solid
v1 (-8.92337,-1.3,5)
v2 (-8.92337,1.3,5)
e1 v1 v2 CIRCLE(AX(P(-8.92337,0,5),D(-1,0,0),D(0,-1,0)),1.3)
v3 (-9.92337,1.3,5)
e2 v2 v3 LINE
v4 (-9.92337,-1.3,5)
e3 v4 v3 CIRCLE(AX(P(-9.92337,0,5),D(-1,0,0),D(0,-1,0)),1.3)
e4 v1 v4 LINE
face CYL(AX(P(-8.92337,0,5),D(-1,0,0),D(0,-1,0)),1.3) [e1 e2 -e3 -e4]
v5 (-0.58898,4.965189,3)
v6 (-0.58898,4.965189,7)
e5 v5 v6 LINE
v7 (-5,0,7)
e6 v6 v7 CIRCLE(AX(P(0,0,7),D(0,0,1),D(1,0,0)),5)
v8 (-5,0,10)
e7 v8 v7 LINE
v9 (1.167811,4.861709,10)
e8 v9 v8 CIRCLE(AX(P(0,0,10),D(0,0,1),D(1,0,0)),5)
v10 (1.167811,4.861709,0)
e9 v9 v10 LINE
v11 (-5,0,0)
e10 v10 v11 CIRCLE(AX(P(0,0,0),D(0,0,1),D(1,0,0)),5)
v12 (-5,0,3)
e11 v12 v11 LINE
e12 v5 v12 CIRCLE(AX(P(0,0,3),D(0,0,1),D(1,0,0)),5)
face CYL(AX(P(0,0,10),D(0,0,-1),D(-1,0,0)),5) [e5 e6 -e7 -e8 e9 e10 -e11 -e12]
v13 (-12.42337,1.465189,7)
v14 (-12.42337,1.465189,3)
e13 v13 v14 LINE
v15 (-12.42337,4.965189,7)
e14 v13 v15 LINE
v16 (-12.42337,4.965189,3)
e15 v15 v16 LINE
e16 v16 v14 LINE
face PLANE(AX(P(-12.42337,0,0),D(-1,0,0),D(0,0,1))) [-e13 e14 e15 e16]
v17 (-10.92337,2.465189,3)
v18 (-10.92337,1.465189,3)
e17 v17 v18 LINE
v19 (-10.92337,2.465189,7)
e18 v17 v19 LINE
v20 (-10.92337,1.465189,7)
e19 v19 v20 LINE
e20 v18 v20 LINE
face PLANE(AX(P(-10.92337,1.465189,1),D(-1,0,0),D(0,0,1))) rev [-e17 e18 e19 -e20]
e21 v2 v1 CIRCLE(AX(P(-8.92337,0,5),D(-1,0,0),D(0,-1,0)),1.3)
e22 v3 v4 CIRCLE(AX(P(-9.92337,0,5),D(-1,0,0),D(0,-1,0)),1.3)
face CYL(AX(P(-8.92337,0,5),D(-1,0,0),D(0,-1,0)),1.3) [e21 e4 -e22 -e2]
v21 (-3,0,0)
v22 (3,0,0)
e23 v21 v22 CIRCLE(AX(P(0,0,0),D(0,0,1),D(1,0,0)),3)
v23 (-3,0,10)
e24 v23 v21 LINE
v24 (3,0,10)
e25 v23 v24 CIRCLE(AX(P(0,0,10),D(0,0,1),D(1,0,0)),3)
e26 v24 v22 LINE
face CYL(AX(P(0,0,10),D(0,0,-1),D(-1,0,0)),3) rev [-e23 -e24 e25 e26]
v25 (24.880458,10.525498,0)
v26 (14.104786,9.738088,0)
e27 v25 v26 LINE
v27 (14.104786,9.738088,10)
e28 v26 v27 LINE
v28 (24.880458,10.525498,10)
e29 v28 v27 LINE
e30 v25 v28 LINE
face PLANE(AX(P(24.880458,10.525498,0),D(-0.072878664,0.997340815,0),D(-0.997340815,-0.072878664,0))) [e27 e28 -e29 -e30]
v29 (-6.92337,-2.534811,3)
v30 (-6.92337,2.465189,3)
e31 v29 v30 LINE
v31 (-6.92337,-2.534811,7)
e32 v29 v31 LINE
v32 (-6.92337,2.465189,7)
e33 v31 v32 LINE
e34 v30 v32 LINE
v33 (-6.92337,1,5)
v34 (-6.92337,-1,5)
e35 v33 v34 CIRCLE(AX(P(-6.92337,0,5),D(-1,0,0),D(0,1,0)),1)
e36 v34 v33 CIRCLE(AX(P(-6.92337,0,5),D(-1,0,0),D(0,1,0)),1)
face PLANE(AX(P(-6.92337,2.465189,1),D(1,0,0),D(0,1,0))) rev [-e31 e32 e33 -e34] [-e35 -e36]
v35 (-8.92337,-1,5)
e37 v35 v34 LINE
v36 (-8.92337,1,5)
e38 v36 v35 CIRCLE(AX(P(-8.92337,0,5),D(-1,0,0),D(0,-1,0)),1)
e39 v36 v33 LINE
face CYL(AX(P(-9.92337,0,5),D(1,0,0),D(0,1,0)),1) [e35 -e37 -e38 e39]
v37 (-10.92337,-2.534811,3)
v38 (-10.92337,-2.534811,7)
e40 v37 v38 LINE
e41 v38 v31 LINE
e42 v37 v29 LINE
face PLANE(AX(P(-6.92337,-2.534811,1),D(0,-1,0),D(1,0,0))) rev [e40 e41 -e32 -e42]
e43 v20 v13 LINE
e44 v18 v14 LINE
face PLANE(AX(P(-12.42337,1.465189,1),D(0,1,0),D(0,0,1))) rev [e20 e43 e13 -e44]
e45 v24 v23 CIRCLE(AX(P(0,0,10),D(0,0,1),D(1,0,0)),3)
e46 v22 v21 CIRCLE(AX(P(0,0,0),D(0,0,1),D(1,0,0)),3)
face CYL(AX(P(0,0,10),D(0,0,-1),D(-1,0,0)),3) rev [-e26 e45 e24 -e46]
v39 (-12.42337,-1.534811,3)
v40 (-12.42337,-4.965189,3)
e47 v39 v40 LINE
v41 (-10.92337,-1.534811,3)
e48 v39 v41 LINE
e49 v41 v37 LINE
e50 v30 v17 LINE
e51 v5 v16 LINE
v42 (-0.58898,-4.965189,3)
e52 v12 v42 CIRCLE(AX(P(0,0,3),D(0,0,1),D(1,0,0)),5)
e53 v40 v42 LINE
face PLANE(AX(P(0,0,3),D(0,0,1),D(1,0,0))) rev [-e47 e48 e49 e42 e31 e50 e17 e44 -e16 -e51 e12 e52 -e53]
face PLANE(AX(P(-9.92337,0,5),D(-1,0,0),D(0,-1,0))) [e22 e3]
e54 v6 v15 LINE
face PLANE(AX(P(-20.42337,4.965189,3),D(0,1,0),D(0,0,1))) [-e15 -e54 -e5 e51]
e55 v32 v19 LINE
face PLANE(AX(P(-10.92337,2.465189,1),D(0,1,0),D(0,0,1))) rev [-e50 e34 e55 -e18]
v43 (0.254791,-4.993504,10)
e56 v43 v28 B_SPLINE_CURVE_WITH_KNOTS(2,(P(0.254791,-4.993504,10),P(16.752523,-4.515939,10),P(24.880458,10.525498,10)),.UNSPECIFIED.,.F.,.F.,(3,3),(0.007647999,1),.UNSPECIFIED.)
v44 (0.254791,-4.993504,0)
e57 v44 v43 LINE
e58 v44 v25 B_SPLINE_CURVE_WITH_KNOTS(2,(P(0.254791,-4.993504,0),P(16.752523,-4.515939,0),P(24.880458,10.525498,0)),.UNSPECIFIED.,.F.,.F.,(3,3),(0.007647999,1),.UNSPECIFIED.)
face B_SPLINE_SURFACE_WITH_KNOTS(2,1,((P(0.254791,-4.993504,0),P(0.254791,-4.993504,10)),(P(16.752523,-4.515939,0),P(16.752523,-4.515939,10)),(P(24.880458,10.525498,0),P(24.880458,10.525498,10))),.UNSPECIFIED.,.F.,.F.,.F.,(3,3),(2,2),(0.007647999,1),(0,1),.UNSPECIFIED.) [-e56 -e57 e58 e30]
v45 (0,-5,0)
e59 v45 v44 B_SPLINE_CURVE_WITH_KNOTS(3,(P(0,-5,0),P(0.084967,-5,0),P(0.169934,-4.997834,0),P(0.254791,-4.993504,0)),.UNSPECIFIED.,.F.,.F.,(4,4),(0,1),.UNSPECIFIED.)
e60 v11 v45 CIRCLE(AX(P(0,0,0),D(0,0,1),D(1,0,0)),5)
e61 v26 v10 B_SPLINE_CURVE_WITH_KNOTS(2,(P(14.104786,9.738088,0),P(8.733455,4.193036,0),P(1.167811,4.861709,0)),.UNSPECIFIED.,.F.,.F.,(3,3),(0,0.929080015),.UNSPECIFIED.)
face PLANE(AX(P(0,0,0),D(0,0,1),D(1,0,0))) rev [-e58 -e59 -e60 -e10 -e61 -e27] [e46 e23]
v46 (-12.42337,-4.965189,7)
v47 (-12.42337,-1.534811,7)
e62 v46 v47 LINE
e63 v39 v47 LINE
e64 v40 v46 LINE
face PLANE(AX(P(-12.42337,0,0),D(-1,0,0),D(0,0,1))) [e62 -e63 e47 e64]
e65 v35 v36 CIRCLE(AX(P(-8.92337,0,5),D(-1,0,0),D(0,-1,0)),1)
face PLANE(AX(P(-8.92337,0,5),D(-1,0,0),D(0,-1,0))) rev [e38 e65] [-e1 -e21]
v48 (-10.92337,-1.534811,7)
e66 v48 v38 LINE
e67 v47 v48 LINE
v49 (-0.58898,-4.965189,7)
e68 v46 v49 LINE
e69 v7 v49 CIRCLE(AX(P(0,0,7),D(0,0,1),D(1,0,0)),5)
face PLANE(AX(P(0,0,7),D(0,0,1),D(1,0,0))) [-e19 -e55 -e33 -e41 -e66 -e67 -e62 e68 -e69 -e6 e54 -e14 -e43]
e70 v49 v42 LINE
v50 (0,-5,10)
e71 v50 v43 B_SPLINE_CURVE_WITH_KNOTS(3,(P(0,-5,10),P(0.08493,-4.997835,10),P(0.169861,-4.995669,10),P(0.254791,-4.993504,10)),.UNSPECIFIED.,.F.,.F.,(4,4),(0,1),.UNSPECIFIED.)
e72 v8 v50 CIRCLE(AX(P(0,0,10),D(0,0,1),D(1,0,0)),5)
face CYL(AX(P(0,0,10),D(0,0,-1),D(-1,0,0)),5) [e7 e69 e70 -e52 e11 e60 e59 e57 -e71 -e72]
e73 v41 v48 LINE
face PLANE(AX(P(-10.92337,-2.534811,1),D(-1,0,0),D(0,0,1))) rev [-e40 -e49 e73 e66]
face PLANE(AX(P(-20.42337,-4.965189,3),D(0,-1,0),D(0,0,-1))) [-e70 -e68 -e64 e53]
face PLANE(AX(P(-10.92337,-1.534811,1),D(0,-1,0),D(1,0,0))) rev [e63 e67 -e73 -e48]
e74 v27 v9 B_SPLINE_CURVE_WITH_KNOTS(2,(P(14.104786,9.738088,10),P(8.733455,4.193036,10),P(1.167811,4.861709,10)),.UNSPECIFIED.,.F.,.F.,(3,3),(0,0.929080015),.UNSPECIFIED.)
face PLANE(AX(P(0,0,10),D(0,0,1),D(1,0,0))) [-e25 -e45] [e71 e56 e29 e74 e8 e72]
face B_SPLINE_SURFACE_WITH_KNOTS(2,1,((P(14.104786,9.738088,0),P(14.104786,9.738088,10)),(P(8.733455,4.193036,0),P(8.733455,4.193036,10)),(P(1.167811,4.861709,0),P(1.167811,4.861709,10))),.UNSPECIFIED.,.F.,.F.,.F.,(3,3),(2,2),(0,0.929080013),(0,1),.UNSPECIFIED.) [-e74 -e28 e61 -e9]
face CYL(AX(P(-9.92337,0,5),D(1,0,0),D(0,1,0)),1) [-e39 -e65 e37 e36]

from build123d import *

# Parameters (mm, degrees)
SKETCH1_R           = 5
SKETCH1_R_2         = 3
BOSS_EXTRUDE1_DEPTH = 10
BOSS_EXTRUDE2_START = -10
SKETCH2_R           = 3
BOSS_EXTRUDE2_DEPTH = 10
BOSS_EXTRUDE3_START = -7
BOSS_EXTRUDE3_DEPTH = 4
SKETCH4_W           = 4
SKETCH4_H           = 9.930378158
CUT_EXTRUDE1_DEPTH  = 8
CUT_EXTRUDE3_DEPTH  = 6
SKETCH7_R           = 1
BOSS_EXTRUDE4_DEPTH = 3
SKETCH8_R           = 1.3
BOSS_EXTRUDE5_DEPTH = 1


with BuildPart() as part:
    # Sketch1 → Boss-Extrude1 (new body)
    with BuildSketch(Plane.XY):
        Circle(SKETCH1_R)
        Circle(SKETCH1_R_2, mode=Mode.SUBTRACT)
    extrude(amount=BOSS_EXTRUDE1_DEPTH)

    # Sketch2 → Boss-Extrude2 (add)
    with BuildSketch(Plane.XY.offset(10).offset(BOSS_EXTRUDE2_START)):
        with BuildLine():
            Line((24.88045834, 10.525498272), (14.10478585, 9.738087788))
            add(Edge.make_bspline(
                [(14.10478585, 9.738087788), (8.323441711, 3.769762394), (0, 5)],
                knots=[0, 0, 0, 1, 1, 1], degree=2))
            ThreePointArc((0, 5), (-5, 0), (0, -5))
            add(Edge.make_bspline(
                [(24.88045834, 10.525498272), (16.689881937, -4.631862586), (0, -5)],
                knots=[0, 0, 0, 1, 1, 1], degree=2))
        make_face()
        Circle(SKETCH2_R, mode=Mode.SUBTRACT)
    extrude(amount=BOSS_EXTRUDE2_DEPTH)

    # Sketch3 → Boss-Extrude3 (add)
    with BuildSketch(Plane.XY.offset(10).offset(BOSS_EXTRUDE3_START)):
        with BuildLine():
            Line((-20.423369766, -4.965189079), (0, -4.965189079))
            Line((0, -4.965189079), (0, -3))
            ThreePointArc((0, -3), (-3, 0), (0, 3))
            Line((0, 3), (0, 4.965189079))
            Line((0, 4.965189079), (-20.423369766, 4.965189079))
            Line((-20.423369766, 4.965189079), (-20.423369766, -4.965189079))
        make_face()
    extrude(amount=BOSS_EXTRUDE3_DEPTH)

    # Sketch4 → Cut-Extrude1 (cut)
    with BuildSketch(Plane.ZY.offset(20.423369766)):
        with Locations((5, 0)):
            Rectangle(SKETCH4_W, SKETCH4_H)
    extrude(amount=-CUT_EXTRUDE1_DEPTH, mode=Mode.SUBTRACT)

    # Sketch6 → Cut-Extrude3 (cut)
    with BuildSketch(Plane.XY.offset(7)):
        Polygon((-12.423369766, 1.465189079), (-10.923369766, 1.465189079), (-10.923369766, 2.465189079), (-6.923369766, 2.465189079), (-6.923369766, -2.534810921), (-10.923369766, -2.534810921), (-10.923369766, -1.534810921), (-12.423369766, -1.534810921), align=None)
    extrude(amount=-CUT_EXTRUDE3_DEPTH, mode=Mode.SUBTRACT)

    # Sketch7 → Boss-Extrude4 (add)
    with BuildSketch(Plane.ZY.offset(6.923369766)):
        with Locations(Location((5, 0, 0), (0, 0, 90))):
            Circle(SKETCH7_R)
    extrude(amount=BOSS_EXTRUDE4_DEPTH)

    # Sketch8 → Boss-Extrude5 (add)
    with BuildSketch(Plane.ZY.offset(9.923369766)):
        with Locations(Location((5, 0, 0), (0, 0, 270))):
            Circle(SKETCH8_R)
    extrude(amount=-BOSS_EXTRUDE5_DEPTH)


solid = part.part
